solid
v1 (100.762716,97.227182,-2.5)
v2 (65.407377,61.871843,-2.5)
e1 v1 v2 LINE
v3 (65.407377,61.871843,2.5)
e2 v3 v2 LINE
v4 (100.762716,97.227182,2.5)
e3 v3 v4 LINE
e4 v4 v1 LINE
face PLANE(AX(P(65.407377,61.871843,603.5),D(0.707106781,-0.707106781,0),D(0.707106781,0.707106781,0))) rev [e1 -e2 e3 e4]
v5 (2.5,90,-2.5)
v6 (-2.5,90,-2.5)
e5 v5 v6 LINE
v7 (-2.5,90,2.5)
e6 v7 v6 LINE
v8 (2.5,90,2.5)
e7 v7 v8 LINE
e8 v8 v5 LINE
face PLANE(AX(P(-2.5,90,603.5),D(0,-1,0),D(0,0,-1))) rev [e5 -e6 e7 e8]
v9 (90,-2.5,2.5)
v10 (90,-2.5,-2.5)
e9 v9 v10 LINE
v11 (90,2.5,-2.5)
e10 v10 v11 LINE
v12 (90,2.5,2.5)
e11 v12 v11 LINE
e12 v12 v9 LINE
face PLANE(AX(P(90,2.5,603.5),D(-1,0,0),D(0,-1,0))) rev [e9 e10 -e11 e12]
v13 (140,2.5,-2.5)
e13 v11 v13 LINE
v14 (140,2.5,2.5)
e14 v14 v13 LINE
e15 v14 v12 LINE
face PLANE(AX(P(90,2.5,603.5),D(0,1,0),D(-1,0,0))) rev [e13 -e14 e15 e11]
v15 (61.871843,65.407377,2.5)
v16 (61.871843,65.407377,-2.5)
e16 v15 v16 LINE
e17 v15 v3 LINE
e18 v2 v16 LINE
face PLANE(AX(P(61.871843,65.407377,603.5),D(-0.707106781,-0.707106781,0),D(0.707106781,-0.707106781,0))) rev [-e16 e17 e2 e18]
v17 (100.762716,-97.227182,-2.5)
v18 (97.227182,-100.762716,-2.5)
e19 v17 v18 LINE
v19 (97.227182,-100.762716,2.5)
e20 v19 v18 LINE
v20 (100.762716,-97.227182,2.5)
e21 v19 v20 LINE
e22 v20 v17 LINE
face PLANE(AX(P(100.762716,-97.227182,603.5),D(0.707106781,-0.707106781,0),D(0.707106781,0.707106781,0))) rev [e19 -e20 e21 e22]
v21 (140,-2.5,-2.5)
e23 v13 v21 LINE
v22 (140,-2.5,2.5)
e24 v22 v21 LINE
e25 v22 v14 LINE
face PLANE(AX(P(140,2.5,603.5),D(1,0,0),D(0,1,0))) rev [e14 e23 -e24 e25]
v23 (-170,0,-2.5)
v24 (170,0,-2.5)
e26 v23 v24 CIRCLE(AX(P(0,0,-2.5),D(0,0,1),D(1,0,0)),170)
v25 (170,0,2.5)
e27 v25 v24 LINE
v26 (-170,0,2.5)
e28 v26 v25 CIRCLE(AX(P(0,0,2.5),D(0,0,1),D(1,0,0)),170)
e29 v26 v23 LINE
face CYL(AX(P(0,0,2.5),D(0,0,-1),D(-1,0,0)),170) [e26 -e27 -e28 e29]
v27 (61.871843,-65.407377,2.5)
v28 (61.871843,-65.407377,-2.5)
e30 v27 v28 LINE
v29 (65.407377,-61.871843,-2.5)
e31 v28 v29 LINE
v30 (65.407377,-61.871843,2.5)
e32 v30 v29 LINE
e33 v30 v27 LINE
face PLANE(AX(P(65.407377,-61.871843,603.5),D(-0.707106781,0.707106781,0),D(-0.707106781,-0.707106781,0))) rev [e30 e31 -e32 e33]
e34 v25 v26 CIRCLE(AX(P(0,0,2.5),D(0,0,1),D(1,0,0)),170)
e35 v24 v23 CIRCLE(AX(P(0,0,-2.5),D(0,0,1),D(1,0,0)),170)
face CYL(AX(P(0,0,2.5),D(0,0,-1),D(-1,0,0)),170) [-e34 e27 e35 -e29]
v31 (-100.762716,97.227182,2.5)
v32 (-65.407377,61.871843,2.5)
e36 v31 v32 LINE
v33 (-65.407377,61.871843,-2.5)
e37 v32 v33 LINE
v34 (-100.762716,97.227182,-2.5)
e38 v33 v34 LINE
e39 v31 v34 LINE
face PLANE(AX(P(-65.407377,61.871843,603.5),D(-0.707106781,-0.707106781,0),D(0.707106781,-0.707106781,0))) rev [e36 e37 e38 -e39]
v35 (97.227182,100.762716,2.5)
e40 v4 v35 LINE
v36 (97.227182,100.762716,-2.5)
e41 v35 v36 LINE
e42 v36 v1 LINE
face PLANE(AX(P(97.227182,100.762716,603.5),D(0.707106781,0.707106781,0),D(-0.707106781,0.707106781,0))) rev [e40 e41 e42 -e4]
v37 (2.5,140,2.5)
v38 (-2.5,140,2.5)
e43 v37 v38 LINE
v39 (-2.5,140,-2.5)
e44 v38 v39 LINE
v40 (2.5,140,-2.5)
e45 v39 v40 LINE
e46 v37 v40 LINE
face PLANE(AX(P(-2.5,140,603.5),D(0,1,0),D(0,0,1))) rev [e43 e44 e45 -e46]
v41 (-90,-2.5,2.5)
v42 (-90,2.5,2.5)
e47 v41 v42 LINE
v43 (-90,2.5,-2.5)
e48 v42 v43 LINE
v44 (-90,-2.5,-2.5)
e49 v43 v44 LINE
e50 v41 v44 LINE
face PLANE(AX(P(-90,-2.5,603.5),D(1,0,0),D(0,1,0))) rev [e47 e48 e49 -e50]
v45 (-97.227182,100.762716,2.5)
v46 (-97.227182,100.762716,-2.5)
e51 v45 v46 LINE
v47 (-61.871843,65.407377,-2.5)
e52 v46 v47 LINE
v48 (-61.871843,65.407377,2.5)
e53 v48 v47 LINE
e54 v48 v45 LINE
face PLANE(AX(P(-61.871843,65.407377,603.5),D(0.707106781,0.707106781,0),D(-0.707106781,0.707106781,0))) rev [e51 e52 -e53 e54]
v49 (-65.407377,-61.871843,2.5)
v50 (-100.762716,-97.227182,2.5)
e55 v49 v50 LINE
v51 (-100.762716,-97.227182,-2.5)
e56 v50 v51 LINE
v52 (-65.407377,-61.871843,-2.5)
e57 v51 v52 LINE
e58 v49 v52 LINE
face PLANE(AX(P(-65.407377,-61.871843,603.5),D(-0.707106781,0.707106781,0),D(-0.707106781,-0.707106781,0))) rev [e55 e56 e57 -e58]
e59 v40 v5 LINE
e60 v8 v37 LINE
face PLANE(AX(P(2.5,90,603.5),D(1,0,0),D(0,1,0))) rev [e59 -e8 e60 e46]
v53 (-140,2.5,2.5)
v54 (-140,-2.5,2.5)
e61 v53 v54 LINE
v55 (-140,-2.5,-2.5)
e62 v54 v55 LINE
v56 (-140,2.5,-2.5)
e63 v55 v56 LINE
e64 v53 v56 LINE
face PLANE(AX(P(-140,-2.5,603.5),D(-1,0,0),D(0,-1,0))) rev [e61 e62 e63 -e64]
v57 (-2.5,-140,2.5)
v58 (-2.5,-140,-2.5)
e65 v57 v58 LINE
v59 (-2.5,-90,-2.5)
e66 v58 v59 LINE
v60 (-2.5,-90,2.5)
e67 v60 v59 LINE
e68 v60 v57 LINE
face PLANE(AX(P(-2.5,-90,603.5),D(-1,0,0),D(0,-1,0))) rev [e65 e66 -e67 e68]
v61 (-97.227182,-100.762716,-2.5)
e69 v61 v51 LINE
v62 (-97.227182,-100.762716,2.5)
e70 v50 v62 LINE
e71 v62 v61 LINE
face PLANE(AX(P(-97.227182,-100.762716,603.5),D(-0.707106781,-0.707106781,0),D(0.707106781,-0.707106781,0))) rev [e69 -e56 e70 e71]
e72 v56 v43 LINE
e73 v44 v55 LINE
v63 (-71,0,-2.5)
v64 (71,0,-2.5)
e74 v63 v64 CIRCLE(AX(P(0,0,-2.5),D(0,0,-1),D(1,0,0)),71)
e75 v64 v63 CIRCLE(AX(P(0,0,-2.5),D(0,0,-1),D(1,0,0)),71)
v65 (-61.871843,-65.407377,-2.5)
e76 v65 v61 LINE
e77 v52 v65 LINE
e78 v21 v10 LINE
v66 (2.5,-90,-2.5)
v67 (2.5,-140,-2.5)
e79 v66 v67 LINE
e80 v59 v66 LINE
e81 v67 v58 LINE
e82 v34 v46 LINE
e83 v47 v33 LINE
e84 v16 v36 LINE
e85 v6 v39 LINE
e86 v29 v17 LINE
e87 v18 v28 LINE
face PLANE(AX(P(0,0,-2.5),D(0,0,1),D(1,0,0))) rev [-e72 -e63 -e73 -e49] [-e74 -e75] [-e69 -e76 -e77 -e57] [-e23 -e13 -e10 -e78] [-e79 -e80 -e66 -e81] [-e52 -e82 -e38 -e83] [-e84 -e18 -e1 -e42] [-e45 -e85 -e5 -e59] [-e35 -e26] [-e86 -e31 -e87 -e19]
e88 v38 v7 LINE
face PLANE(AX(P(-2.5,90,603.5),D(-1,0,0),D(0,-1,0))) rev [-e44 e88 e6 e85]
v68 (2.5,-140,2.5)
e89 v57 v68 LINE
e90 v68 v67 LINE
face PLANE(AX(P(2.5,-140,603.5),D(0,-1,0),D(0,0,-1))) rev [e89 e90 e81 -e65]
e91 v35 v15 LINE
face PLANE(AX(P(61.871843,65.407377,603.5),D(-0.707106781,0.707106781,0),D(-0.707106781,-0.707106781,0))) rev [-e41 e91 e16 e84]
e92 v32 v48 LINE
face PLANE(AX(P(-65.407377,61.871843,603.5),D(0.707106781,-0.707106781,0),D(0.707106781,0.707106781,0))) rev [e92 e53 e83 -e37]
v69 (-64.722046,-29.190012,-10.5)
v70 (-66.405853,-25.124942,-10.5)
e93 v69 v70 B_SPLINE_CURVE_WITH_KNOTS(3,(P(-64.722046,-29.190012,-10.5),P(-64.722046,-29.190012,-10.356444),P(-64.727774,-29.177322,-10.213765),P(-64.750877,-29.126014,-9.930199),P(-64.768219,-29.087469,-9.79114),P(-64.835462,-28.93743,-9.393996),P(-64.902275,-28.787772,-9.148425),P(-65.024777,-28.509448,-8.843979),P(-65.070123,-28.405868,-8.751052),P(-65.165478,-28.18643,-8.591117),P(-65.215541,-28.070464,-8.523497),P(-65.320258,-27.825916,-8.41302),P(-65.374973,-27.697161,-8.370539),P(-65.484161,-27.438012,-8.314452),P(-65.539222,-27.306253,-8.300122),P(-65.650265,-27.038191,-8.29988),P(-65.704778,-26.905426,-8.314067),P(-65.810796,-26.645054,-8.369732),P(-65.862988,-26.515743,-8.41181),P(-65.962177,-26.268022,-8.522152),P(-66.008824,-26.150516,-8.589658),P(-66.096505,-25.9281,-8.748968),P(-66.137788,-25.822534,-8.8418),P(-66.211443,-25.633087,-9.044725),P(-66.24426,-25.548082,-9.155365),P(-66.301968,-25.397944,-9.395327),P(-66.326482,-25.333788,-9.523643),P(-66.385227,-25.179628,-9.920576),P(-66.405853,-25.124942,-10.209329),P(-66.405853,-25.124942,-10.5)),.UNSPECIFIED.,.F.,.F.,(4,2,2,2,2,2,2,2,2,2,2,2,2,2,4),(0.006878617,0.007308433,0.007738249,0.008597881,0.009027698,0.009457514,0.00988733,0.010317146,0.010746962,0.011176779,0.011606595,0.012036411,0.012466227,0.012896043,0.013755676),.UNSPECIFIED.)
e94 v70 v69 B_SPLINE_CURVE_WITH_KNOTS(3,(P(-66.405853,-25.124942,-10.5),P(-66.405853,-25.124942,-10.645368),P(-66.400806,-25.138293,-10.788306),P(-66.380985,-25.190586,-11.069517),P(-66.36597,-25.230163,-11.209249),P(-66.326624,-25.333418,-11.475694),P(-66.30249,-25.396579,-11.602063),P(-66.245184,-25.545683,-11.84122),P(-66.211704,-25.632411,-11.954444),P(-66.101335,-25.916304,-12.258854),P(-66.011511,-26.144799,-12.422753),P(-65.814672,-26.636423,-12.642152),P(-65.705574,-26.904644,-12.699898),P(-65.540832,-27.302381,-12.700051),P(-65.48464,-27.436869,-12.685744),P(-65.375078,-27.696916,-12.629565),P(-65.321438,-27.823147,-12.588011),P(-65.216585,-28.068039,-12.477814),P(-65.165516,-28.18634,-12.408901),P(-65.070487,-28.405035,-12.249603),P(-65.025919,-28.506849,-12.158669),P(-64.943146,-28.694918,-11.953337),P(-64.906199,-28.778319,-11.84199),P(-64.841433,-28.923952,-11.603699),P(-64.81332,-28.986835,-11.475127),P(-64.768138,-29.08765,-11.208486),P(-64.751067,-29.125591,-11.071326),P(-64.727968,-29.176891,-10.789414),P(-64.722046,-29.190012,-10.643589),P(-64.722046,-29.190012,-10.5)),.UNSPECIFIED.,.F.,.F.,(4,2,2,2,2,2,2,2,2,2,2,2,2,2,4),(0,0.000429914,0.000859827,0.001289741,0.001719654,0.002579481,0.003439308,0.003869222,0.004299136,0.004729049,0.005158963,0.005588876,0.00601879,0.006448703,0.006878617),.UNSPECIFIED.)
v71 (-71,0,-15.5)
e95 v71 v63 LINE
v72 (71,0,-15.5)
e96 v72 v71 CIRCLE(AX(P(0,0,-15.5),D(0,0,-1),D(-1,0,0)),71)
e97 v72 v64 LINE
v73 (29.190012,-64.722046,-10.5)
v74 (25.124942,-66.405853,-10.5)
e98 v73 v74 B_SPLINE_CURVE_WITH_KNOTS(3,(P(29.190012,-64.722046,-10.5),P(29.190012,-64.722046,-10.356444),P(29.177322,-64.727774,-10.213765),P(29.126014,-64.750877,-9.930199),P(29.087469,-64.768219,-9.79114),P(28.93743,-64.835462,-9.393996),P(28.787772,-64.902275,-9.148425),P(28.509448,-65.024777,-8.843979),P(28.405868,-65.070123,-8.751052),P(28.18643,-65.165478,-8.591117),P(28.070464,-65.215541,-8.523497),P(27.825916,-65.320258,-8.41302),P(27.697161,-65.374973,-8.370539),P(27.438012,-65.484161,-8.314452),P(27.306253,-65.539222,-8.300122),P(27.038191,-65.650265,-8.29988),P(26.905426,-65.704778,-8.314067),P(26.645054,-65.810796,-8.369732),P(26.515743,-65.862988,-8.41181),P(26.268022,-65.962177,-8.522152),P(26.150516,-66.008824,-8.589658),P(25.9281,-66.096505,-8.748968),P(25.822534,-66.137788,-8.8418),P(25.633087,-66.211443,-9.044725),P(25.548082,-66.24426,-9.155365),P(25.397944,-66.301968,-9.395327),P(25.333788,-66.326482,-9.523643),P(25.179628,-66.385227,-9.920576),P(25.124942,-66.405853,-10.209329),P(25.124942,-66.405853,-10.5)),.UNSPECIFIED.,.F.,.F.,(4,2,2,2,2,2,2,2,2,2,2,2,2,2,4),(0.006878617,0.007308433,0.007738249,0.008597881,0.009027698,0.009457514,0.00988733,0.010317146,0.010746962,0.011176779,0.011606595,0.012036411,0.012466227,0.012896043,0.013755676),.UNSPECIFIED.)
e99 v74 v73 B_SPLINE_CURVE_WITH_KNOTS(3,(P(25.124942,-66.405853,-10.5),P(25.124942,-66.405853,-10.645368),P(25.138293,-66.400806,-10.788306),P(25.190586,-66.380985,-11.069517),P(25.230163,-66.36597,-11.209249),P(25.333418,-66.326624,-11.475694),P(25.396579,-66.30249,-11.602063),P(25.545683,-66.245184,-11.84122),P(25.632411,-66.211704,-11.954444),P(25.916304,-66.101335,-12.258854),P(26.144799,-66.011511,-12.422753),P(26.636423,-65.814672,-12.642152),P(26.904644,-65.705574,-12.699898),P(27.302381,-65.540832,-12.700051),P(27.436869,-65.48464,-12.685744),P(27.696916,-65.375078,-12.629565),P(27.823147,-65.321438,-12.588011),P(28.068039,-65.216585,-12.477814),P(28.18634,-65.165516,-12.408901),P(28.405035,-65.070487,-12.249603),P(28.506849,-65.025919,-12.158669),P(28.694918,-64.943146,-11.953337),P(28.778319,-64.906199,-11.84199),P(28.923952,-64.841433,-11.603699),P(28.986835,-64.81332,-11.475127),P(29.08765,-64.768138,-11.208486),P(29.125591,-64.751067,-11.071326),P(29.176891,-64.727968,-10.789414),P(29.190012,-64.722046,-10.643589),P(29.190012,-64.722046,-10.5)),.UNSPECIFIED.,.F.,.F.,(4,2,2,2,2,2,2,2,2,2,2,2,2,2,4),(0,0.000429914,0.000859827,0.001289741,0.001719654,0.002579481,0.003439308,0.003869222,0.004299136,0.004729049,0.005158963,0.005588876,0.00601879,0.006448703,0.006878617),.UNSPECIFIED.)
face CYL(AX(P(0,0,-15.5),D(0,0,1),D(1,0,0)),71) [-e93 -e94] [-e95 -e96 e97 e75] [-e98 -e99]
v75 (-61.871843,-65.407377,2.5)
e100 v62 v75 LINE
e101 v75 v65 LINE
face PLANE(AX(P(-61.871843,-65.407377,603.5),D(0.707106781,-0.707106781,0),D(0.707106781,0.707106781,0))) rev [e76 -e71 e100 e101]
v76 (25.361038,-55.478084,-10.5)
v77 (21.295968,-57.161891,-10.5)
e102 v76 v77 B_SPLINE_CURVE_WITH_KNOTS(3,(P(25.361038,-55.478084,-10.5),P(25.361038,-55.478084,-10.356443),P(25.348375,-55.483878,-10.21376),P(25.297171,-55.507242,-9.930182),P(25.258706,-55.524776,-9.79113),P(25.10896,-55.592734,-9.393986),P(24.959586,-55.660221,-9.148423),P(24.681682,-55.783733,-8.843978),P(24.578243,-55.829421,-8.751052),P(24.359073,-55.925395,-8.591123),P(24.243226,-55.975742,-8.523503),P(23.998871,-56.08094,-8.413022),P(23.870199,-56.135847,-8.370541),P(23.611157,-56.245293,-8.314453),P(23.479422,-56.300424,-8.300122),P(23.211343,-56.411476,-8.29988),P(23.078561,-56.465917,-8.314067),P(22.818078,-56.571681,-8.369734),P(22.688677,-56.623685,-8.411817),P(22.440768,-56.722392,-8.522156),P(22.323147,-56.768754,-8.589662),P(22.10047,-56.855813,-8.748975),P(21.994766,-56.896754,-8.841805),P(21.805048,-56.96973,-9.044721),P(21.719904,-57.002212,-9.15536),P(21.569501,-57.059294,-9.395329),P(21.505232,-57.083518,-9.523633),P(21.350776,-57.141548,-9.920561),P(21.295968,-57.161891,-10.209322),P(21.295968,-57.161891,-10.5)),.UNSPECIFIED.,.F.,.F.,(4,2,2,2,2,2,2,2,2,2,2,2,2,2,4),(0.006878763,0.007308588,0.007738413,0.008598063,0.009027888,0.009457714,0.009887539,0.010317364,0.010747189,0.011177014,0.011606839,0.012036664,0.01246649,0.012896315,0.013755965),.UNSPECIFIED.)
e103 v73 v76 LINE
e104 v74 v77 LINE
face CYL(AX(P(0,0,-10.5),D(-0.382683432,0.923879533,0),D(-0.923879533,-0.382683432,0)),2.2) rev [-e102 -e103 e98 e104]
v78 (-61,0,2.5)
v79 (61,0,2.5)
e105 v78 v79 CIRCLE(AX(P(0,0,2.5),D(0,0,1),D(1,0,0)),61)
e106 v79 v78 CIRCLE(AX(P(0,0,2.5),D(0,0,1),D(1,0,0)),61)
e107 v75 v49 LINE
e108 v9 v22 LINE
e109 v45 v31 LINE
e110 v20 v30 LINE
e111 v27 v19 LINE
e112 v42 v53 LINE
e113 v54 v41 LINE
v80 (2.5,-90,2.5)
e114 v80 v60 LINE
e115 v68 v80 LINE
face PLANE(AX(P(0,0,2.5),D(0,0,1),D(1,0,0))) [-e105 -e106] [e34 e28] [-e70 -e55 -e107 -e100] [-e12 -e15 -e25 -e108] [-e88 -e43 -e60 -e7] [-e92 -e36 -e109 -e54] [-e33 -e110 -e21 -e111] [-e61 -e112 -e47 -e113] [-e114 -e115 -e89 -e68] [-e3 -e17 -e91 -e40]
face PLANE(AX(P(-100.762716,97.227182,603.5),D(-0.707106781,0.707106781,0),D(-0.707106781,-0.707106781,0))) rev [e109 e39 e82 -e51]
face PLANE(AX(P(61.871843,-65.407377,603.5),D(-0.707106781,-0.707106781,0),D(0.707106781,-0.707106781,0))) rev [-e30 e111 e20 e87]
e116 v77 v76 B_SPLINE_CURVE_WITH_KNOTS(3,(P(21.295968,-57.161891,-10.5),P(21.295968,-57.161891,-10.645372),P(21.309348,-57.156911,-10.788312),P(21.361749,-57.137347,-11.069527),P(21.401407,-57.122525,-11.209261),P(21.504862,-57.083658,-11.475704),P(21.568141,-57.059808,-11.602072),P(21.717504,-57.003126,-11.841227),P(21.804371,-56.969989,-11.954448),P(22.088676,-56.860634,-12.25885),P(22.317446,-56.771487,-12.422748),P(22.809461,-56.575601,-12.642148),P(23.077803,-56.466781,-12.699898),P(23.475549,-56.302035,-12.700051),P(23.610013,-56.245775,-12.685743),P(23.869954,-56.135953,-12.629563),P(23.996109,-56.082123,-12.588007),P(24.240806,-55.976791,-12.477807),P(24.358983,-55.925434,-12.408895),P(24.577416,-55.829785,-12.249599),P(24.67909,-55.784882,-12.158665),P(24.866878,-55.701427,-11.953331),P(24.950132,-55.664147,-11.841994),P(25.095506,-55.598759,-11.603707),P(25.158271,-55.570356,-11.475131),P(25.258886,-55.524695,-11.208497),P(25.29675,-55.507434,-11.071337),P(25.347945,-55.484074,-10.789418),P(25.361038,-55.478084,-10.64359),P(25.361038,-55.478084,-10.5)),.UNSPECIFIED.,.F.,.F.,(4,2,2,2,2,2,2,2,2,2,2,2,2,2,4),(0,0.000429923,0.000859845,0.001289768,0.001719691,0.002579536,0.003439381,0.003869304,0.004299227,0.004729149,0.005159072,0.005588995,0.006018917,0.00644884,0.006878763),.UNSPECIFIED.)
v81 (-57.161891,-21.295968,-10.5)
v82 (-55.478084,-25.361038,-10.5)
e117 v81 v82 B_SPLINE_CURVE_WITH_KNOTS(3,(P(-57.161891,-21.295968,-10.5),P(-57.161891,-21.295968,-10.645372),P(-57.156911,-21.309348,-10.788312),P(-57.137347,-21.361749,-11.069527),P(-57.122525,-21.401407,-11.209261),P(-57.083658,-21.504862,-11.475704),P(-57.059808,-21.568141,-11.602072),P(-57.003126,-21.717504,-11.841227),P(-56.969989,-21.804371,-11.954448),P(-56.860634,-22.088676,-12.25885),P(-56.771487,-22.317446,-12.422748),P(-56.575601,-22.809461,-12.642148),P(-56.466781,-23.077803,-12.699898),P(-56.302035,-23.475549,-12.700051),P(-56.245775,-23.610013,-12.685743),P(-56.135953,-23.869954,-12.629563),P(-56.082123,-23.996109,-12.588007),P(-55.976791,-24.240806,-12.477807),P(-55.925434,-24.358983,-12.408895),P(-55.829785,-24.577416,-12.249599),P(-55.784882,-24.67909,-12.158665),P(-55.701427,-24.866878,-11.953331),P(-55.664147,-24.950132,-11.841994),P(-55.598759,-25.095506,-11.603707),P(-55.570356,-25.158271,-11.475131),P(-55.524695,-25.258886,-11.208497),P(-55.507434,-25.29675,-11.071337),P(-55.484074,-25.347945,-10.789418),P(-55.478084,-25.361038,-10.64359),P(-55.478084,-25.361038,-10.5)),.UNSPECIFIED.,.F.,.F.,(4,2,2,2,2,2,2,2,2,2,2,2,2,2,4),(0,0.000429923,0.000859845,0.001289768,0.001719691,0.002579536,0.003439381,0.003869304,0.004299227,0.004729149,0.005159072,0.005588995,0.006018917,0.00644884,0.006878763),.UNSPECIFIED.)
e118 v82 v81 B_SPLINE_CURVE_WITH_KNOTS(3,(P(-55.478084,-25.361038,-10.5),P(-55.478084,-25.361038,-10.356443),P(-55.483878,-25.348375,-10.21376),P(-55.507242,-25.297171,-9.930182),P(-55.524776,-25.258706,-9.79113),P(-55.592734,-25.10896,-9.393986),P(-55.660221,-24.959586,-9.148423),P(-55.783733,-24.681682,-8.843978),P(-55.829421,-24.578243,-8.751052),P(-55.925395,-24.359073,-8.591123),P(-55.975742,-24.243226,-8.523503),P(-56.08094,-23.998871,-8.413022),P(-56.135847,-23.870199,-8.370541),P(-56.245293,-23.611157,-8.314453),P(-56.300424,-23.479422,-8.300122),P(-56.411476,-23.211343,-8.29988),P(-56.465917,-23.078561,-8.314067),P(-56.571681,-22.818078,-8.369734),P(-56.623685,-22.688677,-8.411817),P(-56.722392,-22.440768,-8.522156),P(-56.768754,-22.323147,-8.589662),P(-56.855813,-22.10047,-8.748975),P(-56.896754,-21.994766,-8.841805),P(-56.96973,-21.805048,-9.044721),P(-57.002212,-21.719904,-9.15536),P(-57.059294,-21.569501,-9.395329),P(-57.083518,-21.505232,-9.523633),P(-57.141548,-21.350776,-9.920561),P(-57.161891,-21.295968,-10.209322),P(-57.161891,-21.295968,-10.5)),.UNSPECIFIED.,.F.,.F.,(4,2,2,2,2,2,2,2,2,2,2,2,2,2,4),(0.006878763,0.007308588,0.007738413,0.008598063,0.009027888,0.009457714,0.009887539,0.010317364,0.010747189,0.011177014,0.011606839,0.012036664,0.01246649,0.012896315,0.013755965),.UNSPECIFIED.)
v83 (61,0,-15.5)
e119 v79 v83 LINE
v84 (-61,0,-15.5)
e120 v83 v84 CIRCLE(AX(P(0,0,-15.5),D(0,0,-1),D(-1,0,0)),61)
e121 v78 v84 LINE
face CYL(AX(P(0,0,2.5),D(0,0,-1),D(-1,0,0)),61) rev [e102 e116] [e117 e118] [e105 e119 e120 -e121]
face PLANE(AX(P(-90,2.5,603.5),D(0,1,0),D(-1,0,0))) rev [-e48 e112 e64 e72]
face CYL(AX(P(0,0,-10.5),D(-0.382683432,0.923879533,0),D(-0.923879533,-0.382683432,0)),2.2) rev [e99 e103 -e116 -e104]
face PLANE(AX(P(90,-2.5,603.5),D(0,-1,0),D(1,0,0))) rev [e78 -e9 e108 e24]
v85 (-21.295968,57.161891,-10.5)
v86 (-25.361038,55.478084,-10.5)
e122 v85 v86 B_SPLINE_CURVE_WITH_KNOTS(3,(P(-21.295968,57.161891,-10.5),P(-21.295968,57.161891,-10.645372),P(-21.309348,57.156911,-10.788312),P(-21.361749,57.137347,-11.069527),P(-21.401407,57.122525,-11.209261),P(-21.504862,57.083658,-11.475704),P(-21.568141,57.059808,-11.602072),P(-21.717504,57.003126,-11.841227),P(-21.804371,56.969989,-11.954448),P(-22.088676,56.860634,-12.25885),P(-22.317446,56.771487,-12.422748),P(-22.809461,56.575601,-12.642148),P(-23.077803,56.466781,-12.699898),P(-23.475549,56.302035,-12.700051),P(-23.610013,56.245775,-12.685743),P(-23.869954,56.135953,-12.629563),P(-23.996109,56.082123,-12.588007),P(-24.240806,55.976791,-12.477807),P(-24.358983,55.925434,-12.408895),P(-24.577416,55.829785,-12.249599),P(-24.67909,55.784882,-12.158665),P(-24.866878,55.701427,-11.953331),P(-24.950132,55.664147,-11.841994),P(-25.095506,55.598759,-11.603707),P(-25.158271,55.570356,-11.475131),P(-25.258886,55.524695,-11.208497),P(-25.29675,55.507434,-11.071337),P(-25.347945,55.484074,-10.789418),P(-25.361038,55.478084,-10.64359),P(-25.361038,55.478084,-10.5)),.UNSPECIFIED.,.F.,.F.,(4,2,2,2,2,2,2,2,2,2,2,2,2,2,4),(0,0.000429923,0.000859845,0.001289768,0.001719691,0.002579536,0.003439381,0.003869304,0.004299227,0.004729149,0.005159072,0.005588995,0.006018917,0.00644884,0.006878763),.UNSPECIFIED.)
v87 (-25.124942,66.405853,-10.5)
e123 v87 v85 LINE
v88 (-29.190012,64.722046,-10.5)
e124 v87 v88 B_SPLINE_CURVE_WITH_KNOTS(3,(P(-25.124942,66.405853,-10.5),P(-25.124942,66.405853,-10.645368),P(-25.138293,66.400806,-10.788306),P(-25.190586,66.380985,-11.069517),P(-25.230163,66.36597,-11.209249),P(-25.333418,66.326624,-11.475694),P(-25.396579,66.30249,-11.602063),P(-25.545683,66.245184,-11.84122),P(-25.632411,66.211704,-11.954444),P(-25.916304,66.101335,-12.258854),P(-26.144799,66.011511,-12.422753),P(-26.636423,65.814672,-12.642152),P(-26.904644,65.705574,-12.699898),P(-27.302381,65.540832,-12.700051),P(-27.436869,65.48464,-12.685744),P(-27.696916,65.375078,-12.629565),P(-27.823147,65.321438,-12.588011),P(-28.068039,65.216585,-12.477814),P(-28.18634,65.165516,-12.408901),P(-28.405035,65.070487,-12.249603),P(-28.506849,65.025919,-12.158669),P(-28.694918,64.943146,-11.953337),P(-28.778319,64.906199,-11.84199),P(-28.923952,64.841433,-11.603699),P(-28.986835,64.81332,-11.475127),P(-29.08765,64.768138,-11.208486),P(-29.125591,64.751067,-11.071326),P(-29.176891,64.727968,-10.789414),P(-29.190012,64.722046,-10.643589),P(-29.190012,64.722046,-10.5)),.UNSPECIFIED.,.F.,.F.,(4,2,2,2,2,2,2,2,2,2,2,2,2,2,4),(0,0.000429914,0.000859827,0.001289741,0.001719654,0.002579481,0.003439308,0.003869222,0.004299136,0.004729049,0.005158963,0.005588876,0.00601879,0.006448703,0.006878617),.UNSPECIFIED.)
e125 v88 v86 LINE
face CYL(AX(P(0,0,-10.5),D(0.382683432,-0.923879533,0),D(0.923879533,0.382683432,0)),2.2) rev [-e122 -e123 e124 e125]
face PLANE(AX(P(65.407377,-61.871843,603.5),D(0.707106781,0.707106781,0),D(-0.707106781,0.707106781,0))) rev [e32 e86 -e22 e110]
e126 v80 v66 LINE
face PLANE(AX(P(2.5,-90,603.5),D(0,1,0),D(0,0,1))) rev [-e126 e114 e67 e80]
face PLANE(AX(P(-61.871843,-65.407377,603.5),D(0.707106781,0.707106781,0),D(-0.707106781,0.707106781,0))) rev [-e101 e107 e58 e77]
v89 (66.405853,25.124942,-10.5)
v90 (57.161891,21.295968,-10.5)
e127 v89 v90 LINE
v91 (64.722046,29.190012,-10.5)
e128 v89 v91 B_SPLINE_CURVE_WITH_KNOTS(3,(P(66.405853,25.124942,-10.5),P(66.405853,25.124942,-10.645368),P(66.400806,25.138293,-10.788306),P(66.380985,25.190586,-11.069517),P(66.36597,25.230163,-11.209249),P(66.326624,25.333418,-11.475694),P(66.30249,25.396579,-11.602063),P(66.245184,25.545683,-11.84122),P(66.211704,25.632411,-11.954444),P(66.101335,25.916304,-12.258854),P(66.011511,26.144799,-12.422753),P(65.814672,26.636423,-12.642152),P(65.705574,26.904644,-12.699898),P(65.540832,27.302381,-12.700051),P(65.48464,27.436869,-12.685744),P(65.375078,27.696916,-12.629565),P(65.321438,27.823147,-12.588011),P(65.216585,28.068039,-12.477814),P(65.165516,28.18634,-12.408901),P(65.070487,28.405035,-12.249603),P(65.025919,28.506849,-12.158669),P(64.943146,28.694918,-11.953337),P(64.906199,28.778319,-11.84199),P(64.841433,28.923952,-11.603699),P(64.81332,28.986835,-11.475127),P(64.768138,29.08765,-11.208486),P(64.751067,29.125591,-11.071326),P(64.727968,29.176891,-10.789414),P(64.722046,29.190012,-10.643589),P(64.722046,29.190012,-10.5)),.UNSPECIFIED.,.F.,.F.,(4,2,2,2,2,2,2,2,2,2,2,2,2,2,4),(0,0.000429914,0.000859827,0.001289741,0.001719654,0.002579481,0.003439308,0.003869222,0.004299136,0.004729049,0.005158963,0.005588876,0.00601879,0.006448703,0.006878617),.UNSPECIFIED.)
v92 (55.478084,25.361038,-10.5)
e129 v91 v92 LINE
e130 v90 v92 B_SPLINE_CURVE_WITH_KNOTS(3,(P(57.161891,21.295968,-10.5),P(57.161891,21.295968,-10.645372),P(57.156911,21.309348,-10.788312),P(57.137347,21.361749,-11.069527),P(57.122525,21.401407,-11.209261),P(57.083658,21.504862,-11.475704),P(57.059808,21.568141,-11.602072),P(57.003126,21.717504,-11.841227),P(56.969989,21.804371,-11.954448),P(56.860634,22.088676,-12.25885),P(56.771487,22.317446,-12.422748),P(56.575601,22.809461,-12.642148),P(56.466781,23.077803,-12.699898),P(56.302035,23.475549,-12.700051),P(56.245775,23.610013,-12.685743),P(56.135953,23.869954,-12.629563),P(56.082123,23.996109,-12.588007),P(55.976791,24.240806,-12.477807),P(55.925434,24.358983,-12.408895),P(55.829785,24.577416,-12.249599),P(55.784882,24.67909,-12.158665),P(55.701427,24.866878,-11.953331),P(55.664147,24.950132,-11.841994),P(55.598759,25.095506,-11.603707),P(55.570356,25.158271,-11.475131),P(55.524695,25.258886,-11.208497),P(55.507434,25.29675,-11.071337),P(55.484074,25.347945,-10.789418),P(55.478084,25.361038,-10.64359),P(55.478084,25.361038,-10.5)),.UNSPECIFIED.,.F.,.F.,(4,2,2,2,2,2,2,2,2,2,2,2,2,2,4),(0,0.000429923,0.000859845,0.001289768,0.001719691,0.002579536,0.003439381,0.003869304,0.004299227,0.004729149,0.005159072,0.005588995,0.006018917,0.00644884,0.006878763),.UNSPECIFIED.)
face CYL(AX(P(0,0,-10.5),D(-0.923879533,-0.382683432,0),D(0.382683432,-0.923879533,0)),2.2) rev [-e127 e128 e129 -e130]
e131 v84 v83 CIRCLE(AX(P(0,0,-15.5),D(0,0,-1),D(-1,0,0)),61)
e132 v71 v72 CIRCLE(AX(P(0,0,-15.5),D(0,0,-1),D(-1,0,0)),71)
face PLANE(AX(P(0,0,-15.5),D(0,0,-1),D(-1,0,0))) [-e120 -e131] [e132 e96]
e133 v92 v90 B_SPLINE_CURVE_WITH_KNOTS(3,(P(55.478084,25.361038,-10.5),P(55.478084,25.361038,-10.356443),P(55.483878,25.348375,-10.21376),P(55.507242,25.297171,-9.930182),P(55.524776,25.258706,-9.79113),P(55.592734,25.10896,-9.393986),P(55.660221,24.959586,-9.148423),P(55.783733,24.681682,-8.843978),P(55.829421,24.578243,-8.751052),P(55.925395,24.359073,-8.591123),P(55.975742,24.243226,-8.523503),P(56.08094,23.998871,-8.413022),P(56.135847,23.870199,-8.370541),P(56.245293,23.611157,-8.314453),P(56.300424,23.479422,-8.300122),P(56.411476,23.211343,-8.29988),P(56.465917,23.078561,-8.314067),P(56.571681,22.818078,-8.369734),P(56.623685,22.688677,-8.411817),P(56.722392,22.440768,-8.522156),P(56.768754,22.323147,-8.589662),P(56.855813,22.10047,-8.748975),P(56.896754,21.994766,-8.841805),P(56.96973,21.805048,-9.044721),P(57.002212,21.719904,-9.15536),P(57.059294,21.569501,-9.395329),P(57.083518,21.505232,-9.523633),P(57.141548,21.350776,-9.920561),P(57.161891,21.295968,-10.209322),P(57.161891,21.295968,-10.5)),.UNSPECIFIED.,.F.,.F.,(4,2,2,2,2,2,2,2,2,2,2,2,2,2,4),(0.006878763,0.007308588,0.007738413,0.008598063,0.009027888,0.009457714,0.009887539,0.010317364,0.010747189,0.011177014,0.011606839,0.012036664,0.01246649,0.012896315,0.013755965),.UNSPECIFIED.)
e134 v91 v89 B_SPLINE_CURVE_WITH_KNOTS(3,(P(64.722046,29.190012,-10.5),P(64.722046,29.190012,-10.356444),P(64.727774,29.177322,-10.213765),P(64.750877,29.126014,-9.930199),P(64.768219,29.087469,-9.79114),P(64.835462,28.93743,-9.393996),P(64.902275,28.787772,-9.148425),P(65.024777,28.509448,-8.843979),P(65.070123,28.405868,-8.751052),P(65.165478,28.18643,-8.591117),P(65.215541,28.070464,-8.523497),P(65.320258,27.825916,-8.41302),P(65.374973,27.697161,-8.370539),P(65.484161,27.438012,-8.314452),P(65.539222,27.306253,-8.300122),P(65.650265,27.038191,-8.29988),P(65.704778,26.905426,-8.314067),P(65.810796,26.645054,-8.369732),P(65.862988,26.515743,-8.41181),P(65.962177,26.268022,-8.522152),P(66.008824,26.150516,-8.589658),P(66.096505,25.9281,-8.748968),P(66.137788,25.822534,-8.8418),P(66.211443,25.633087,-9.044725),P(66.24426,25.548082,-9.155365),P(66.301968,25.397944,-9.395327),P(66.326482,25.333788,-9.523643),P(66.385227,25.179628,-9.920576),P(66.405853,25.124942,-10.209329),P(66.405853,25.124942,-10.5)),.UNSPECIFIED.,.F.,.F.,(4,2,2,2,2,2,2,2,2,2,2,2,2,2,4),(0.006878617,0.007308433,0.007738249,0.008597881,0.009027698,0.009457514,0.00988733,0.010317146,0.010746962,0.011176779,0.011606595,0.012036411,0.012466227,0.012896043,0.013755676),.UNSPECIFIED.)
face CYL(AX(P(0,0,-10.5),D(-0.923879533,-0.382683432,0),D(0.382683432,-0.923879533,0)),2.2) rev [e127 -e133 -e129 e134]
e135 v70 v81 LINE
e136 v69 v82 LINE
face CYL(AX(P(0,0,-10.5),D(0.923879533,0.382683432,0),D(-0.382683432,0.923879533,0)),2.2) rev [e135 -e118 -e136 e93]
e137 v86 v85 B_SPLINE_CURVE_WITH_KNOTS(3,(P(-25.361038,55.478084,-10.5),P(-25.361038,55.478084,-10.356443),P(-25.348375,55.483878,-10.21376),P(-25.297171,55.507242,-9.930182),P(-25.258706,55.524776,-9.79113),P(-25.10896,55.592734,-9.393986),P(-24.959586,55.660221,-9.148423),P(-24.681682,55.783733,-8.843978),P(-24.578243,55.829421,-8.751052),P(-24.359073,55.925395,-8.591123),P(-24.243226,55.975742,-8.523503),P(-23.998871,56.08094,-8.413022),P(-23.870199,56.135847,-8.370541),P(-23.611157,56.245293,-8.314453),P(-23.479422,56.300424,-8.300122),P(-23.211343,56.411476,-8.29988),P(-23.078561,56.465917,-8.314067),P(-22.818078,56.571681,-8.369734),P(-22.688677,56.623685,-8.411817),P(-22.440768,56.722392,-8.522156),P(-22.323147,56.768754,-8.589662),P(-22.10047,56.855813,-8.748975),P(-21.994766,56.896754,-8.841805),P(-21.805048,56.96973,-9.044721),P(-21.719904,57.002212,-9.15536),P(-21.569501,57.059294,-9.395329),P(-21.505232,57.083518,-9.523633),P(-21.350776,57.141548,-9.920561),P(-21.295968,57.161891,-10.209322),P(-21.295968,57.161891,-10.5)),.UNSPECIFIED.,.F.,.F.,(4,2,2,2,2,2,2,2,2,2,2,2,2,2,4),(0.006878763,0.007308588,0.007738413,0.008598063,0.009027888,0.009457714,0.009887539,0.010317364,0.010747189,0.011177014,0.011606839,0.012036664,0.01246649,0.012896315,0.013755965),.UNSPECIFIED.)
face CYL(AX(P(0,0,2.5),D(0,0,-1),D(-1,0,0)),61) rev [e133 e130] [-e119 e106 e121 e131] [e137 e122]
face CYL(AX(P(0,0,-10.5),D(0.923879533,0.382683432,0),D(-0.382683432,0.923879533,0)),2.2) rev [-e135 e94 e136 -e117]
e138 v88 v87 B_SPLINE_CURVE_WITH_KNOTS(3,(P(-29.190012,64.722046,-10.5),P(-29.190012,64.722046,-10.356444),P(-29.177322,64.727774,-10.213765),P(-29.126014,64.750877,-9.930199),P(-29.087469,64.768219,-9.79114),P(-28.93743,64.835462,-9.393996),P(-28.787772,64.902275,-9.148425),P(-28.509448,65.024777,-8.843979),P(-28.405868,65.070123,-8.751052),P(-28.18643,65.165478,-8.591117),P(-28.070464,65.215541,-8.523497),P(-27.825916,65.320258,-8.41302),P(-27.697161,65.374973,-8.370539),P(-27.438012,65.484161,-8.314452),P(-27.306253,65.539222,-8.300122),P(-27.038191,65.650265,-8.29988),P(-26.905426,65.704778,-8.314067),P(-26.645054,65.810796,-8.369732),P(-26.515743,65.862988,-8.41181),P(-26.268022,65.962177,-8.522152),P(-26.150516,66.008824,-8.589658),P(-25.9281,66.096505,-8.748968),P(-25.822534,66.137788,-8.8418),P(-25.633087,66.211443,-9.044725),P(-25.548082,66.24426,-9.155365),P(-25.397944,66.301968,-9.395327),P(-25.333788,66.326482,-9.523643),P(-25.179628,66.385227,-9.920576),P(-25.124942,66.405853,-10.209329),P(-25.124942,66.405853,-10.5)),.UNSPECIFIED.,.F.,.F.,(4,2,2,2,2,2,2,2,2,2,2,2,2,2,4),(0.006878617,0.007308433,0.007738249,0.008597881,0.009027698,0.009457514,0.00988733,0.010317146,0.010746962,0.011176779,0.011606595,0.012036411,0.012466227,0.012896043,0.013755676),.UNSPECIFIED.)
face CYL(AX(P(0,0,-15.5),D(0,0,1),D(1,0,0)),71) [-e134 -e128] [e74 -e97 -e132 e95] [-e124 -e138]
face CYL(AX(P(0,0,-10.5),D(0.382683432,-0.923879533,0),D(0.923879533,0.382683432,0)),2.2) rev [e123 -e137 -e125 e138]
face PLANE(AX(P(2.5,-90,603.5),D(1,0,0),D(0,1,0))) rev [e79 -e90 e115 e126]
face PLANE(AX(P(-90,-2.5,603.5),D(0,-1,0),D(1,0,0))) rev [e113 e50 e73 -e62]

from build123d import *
from build123d.topology import SkipClean

# Parameters (mm, degrees)
SKETCH_1_R               = 170
SKETCH_1_R_2             = 61
EXTRUDE_1_DEPTH          = 2.5
SKETCH_2_W               = 5
SKETCH_2_H               = 50
CUT_EXTRUDE_1_DEPTH      = 606
PATTERN_CIRCULAR_1_COUNT = 8
EXTRUDE_START            = 13
SKETCH_3_R               = 71
SKETCH_3_R_2             = 61
EXTRUDE_2_DEPTH          = 13
PATTERN_CIRCULAR_2_COUNT = 4


with BuildPart() as part:
    # 草图1 → 凸台-拉伸1 (new, symmetric)
    with BuildSketch(Plane.XY):
        Circle(SKETCH_1_R)
        Circle(SKETCH_1_R_2, mode=Mode.SUBTRACT)
    extrude(amount=EXTRUDE_1_DEPTH, both=True)

    # 草图2 → 切除-拉伸1 (cut)
    with BuildSketch(Plane(origin=(0, 0, -2.5), x_dir=(-1, 0, 0), z_dir=(0, 0, -1))):
        with Locations((0, 115)):
            Rectangle(SKETCH_2_W, SKETCH_2_H)
    cut_extrude_1 = extrude(amount=-CUT_EXTRUDE_1_DEPTH, mode=Mode.SUBTRACT)

    # 阵列(圆周)1: 切除-拉伸1 ×8 about axis
    pattern_circular_1_axis = Axis((0, 0, 0), (0, 0, 1))
    for i in range(1, PATTERN_CIRCULAR_1_COUNT):
        add(cut_extrude_1.rotate(pattern_circular_1_axis, i * 360 / PATTERN_CIRCULAR_1_COUNT), mode=Mode.SUBTRACT)

    # 草图3 → 凸台-拉伸2 (add)
    with SkipClean():  # the faces are left unmerged after this step: merging them gives an invalid solid
        with BuildSketch(Plane(origin=(0, 0, -2.5), x_dir=(-1, 0, 0), z_dir=(0, 0, -1)).offset(EXTRUDE_START)):
            with Locations(Location((0, 0, 0), (0, 0, 180))):
                Circle(SKETCH_3_R)
            Circle(SKETCH_3_R_2, mode=Mode.SUBTRACT)
        extrude(amount=-EXTRUDE_2_DEPTH)

    # 草图4 → 切除-旋转1 (revolve, cut)
    with SkipClean():  # the faces are left unmerged after this step: merging them gives an invalid solid
        with BuildSketch(Plane(origin=(0, 0, -10.5), x_dir=(-1, 0, 0), z_dir=(0, 0, -1)), mode=Mode.PRIVATE) as cut_revolve_1_sk:
            Polygon((34.991643562, 78.728423411), (32.95910859, 79.570326962), (17.162768918, 41.434589489), (19.195303889, 40.592685937), align=None)
        cut_revolve_1 = revolve(cut_revolve_1_sk.sketch.rotate(Axis((0, 0, -10.5), (-0.38268343236509056, 0.9238795325112865, 0)), 180), axis=Axis((0, 0, -10.5), (-0.38268343236509056, 0.9238795325112865, 0)), mode=Mode.SUBTRACT)

    # 阵列(圆周)2: 切除-旋转1 ×4 about axis
    with SkipClean():  # the faces are left unmerged after this step: merging them gives an invalid solid
        pattern_circular_2_axis = Axis((0, 0, 2.5), (0, 0, -1))
        for i in range(1, PATTERN_CIRCULAR_2_COUNT):
            add(cut_revolve_1.rotate(pattern_circular_2_axis, i * 360 / PATTERN_CIRCULAR_2_COUNT), mode=Mode.SUBTRACT)


solid = part.part
